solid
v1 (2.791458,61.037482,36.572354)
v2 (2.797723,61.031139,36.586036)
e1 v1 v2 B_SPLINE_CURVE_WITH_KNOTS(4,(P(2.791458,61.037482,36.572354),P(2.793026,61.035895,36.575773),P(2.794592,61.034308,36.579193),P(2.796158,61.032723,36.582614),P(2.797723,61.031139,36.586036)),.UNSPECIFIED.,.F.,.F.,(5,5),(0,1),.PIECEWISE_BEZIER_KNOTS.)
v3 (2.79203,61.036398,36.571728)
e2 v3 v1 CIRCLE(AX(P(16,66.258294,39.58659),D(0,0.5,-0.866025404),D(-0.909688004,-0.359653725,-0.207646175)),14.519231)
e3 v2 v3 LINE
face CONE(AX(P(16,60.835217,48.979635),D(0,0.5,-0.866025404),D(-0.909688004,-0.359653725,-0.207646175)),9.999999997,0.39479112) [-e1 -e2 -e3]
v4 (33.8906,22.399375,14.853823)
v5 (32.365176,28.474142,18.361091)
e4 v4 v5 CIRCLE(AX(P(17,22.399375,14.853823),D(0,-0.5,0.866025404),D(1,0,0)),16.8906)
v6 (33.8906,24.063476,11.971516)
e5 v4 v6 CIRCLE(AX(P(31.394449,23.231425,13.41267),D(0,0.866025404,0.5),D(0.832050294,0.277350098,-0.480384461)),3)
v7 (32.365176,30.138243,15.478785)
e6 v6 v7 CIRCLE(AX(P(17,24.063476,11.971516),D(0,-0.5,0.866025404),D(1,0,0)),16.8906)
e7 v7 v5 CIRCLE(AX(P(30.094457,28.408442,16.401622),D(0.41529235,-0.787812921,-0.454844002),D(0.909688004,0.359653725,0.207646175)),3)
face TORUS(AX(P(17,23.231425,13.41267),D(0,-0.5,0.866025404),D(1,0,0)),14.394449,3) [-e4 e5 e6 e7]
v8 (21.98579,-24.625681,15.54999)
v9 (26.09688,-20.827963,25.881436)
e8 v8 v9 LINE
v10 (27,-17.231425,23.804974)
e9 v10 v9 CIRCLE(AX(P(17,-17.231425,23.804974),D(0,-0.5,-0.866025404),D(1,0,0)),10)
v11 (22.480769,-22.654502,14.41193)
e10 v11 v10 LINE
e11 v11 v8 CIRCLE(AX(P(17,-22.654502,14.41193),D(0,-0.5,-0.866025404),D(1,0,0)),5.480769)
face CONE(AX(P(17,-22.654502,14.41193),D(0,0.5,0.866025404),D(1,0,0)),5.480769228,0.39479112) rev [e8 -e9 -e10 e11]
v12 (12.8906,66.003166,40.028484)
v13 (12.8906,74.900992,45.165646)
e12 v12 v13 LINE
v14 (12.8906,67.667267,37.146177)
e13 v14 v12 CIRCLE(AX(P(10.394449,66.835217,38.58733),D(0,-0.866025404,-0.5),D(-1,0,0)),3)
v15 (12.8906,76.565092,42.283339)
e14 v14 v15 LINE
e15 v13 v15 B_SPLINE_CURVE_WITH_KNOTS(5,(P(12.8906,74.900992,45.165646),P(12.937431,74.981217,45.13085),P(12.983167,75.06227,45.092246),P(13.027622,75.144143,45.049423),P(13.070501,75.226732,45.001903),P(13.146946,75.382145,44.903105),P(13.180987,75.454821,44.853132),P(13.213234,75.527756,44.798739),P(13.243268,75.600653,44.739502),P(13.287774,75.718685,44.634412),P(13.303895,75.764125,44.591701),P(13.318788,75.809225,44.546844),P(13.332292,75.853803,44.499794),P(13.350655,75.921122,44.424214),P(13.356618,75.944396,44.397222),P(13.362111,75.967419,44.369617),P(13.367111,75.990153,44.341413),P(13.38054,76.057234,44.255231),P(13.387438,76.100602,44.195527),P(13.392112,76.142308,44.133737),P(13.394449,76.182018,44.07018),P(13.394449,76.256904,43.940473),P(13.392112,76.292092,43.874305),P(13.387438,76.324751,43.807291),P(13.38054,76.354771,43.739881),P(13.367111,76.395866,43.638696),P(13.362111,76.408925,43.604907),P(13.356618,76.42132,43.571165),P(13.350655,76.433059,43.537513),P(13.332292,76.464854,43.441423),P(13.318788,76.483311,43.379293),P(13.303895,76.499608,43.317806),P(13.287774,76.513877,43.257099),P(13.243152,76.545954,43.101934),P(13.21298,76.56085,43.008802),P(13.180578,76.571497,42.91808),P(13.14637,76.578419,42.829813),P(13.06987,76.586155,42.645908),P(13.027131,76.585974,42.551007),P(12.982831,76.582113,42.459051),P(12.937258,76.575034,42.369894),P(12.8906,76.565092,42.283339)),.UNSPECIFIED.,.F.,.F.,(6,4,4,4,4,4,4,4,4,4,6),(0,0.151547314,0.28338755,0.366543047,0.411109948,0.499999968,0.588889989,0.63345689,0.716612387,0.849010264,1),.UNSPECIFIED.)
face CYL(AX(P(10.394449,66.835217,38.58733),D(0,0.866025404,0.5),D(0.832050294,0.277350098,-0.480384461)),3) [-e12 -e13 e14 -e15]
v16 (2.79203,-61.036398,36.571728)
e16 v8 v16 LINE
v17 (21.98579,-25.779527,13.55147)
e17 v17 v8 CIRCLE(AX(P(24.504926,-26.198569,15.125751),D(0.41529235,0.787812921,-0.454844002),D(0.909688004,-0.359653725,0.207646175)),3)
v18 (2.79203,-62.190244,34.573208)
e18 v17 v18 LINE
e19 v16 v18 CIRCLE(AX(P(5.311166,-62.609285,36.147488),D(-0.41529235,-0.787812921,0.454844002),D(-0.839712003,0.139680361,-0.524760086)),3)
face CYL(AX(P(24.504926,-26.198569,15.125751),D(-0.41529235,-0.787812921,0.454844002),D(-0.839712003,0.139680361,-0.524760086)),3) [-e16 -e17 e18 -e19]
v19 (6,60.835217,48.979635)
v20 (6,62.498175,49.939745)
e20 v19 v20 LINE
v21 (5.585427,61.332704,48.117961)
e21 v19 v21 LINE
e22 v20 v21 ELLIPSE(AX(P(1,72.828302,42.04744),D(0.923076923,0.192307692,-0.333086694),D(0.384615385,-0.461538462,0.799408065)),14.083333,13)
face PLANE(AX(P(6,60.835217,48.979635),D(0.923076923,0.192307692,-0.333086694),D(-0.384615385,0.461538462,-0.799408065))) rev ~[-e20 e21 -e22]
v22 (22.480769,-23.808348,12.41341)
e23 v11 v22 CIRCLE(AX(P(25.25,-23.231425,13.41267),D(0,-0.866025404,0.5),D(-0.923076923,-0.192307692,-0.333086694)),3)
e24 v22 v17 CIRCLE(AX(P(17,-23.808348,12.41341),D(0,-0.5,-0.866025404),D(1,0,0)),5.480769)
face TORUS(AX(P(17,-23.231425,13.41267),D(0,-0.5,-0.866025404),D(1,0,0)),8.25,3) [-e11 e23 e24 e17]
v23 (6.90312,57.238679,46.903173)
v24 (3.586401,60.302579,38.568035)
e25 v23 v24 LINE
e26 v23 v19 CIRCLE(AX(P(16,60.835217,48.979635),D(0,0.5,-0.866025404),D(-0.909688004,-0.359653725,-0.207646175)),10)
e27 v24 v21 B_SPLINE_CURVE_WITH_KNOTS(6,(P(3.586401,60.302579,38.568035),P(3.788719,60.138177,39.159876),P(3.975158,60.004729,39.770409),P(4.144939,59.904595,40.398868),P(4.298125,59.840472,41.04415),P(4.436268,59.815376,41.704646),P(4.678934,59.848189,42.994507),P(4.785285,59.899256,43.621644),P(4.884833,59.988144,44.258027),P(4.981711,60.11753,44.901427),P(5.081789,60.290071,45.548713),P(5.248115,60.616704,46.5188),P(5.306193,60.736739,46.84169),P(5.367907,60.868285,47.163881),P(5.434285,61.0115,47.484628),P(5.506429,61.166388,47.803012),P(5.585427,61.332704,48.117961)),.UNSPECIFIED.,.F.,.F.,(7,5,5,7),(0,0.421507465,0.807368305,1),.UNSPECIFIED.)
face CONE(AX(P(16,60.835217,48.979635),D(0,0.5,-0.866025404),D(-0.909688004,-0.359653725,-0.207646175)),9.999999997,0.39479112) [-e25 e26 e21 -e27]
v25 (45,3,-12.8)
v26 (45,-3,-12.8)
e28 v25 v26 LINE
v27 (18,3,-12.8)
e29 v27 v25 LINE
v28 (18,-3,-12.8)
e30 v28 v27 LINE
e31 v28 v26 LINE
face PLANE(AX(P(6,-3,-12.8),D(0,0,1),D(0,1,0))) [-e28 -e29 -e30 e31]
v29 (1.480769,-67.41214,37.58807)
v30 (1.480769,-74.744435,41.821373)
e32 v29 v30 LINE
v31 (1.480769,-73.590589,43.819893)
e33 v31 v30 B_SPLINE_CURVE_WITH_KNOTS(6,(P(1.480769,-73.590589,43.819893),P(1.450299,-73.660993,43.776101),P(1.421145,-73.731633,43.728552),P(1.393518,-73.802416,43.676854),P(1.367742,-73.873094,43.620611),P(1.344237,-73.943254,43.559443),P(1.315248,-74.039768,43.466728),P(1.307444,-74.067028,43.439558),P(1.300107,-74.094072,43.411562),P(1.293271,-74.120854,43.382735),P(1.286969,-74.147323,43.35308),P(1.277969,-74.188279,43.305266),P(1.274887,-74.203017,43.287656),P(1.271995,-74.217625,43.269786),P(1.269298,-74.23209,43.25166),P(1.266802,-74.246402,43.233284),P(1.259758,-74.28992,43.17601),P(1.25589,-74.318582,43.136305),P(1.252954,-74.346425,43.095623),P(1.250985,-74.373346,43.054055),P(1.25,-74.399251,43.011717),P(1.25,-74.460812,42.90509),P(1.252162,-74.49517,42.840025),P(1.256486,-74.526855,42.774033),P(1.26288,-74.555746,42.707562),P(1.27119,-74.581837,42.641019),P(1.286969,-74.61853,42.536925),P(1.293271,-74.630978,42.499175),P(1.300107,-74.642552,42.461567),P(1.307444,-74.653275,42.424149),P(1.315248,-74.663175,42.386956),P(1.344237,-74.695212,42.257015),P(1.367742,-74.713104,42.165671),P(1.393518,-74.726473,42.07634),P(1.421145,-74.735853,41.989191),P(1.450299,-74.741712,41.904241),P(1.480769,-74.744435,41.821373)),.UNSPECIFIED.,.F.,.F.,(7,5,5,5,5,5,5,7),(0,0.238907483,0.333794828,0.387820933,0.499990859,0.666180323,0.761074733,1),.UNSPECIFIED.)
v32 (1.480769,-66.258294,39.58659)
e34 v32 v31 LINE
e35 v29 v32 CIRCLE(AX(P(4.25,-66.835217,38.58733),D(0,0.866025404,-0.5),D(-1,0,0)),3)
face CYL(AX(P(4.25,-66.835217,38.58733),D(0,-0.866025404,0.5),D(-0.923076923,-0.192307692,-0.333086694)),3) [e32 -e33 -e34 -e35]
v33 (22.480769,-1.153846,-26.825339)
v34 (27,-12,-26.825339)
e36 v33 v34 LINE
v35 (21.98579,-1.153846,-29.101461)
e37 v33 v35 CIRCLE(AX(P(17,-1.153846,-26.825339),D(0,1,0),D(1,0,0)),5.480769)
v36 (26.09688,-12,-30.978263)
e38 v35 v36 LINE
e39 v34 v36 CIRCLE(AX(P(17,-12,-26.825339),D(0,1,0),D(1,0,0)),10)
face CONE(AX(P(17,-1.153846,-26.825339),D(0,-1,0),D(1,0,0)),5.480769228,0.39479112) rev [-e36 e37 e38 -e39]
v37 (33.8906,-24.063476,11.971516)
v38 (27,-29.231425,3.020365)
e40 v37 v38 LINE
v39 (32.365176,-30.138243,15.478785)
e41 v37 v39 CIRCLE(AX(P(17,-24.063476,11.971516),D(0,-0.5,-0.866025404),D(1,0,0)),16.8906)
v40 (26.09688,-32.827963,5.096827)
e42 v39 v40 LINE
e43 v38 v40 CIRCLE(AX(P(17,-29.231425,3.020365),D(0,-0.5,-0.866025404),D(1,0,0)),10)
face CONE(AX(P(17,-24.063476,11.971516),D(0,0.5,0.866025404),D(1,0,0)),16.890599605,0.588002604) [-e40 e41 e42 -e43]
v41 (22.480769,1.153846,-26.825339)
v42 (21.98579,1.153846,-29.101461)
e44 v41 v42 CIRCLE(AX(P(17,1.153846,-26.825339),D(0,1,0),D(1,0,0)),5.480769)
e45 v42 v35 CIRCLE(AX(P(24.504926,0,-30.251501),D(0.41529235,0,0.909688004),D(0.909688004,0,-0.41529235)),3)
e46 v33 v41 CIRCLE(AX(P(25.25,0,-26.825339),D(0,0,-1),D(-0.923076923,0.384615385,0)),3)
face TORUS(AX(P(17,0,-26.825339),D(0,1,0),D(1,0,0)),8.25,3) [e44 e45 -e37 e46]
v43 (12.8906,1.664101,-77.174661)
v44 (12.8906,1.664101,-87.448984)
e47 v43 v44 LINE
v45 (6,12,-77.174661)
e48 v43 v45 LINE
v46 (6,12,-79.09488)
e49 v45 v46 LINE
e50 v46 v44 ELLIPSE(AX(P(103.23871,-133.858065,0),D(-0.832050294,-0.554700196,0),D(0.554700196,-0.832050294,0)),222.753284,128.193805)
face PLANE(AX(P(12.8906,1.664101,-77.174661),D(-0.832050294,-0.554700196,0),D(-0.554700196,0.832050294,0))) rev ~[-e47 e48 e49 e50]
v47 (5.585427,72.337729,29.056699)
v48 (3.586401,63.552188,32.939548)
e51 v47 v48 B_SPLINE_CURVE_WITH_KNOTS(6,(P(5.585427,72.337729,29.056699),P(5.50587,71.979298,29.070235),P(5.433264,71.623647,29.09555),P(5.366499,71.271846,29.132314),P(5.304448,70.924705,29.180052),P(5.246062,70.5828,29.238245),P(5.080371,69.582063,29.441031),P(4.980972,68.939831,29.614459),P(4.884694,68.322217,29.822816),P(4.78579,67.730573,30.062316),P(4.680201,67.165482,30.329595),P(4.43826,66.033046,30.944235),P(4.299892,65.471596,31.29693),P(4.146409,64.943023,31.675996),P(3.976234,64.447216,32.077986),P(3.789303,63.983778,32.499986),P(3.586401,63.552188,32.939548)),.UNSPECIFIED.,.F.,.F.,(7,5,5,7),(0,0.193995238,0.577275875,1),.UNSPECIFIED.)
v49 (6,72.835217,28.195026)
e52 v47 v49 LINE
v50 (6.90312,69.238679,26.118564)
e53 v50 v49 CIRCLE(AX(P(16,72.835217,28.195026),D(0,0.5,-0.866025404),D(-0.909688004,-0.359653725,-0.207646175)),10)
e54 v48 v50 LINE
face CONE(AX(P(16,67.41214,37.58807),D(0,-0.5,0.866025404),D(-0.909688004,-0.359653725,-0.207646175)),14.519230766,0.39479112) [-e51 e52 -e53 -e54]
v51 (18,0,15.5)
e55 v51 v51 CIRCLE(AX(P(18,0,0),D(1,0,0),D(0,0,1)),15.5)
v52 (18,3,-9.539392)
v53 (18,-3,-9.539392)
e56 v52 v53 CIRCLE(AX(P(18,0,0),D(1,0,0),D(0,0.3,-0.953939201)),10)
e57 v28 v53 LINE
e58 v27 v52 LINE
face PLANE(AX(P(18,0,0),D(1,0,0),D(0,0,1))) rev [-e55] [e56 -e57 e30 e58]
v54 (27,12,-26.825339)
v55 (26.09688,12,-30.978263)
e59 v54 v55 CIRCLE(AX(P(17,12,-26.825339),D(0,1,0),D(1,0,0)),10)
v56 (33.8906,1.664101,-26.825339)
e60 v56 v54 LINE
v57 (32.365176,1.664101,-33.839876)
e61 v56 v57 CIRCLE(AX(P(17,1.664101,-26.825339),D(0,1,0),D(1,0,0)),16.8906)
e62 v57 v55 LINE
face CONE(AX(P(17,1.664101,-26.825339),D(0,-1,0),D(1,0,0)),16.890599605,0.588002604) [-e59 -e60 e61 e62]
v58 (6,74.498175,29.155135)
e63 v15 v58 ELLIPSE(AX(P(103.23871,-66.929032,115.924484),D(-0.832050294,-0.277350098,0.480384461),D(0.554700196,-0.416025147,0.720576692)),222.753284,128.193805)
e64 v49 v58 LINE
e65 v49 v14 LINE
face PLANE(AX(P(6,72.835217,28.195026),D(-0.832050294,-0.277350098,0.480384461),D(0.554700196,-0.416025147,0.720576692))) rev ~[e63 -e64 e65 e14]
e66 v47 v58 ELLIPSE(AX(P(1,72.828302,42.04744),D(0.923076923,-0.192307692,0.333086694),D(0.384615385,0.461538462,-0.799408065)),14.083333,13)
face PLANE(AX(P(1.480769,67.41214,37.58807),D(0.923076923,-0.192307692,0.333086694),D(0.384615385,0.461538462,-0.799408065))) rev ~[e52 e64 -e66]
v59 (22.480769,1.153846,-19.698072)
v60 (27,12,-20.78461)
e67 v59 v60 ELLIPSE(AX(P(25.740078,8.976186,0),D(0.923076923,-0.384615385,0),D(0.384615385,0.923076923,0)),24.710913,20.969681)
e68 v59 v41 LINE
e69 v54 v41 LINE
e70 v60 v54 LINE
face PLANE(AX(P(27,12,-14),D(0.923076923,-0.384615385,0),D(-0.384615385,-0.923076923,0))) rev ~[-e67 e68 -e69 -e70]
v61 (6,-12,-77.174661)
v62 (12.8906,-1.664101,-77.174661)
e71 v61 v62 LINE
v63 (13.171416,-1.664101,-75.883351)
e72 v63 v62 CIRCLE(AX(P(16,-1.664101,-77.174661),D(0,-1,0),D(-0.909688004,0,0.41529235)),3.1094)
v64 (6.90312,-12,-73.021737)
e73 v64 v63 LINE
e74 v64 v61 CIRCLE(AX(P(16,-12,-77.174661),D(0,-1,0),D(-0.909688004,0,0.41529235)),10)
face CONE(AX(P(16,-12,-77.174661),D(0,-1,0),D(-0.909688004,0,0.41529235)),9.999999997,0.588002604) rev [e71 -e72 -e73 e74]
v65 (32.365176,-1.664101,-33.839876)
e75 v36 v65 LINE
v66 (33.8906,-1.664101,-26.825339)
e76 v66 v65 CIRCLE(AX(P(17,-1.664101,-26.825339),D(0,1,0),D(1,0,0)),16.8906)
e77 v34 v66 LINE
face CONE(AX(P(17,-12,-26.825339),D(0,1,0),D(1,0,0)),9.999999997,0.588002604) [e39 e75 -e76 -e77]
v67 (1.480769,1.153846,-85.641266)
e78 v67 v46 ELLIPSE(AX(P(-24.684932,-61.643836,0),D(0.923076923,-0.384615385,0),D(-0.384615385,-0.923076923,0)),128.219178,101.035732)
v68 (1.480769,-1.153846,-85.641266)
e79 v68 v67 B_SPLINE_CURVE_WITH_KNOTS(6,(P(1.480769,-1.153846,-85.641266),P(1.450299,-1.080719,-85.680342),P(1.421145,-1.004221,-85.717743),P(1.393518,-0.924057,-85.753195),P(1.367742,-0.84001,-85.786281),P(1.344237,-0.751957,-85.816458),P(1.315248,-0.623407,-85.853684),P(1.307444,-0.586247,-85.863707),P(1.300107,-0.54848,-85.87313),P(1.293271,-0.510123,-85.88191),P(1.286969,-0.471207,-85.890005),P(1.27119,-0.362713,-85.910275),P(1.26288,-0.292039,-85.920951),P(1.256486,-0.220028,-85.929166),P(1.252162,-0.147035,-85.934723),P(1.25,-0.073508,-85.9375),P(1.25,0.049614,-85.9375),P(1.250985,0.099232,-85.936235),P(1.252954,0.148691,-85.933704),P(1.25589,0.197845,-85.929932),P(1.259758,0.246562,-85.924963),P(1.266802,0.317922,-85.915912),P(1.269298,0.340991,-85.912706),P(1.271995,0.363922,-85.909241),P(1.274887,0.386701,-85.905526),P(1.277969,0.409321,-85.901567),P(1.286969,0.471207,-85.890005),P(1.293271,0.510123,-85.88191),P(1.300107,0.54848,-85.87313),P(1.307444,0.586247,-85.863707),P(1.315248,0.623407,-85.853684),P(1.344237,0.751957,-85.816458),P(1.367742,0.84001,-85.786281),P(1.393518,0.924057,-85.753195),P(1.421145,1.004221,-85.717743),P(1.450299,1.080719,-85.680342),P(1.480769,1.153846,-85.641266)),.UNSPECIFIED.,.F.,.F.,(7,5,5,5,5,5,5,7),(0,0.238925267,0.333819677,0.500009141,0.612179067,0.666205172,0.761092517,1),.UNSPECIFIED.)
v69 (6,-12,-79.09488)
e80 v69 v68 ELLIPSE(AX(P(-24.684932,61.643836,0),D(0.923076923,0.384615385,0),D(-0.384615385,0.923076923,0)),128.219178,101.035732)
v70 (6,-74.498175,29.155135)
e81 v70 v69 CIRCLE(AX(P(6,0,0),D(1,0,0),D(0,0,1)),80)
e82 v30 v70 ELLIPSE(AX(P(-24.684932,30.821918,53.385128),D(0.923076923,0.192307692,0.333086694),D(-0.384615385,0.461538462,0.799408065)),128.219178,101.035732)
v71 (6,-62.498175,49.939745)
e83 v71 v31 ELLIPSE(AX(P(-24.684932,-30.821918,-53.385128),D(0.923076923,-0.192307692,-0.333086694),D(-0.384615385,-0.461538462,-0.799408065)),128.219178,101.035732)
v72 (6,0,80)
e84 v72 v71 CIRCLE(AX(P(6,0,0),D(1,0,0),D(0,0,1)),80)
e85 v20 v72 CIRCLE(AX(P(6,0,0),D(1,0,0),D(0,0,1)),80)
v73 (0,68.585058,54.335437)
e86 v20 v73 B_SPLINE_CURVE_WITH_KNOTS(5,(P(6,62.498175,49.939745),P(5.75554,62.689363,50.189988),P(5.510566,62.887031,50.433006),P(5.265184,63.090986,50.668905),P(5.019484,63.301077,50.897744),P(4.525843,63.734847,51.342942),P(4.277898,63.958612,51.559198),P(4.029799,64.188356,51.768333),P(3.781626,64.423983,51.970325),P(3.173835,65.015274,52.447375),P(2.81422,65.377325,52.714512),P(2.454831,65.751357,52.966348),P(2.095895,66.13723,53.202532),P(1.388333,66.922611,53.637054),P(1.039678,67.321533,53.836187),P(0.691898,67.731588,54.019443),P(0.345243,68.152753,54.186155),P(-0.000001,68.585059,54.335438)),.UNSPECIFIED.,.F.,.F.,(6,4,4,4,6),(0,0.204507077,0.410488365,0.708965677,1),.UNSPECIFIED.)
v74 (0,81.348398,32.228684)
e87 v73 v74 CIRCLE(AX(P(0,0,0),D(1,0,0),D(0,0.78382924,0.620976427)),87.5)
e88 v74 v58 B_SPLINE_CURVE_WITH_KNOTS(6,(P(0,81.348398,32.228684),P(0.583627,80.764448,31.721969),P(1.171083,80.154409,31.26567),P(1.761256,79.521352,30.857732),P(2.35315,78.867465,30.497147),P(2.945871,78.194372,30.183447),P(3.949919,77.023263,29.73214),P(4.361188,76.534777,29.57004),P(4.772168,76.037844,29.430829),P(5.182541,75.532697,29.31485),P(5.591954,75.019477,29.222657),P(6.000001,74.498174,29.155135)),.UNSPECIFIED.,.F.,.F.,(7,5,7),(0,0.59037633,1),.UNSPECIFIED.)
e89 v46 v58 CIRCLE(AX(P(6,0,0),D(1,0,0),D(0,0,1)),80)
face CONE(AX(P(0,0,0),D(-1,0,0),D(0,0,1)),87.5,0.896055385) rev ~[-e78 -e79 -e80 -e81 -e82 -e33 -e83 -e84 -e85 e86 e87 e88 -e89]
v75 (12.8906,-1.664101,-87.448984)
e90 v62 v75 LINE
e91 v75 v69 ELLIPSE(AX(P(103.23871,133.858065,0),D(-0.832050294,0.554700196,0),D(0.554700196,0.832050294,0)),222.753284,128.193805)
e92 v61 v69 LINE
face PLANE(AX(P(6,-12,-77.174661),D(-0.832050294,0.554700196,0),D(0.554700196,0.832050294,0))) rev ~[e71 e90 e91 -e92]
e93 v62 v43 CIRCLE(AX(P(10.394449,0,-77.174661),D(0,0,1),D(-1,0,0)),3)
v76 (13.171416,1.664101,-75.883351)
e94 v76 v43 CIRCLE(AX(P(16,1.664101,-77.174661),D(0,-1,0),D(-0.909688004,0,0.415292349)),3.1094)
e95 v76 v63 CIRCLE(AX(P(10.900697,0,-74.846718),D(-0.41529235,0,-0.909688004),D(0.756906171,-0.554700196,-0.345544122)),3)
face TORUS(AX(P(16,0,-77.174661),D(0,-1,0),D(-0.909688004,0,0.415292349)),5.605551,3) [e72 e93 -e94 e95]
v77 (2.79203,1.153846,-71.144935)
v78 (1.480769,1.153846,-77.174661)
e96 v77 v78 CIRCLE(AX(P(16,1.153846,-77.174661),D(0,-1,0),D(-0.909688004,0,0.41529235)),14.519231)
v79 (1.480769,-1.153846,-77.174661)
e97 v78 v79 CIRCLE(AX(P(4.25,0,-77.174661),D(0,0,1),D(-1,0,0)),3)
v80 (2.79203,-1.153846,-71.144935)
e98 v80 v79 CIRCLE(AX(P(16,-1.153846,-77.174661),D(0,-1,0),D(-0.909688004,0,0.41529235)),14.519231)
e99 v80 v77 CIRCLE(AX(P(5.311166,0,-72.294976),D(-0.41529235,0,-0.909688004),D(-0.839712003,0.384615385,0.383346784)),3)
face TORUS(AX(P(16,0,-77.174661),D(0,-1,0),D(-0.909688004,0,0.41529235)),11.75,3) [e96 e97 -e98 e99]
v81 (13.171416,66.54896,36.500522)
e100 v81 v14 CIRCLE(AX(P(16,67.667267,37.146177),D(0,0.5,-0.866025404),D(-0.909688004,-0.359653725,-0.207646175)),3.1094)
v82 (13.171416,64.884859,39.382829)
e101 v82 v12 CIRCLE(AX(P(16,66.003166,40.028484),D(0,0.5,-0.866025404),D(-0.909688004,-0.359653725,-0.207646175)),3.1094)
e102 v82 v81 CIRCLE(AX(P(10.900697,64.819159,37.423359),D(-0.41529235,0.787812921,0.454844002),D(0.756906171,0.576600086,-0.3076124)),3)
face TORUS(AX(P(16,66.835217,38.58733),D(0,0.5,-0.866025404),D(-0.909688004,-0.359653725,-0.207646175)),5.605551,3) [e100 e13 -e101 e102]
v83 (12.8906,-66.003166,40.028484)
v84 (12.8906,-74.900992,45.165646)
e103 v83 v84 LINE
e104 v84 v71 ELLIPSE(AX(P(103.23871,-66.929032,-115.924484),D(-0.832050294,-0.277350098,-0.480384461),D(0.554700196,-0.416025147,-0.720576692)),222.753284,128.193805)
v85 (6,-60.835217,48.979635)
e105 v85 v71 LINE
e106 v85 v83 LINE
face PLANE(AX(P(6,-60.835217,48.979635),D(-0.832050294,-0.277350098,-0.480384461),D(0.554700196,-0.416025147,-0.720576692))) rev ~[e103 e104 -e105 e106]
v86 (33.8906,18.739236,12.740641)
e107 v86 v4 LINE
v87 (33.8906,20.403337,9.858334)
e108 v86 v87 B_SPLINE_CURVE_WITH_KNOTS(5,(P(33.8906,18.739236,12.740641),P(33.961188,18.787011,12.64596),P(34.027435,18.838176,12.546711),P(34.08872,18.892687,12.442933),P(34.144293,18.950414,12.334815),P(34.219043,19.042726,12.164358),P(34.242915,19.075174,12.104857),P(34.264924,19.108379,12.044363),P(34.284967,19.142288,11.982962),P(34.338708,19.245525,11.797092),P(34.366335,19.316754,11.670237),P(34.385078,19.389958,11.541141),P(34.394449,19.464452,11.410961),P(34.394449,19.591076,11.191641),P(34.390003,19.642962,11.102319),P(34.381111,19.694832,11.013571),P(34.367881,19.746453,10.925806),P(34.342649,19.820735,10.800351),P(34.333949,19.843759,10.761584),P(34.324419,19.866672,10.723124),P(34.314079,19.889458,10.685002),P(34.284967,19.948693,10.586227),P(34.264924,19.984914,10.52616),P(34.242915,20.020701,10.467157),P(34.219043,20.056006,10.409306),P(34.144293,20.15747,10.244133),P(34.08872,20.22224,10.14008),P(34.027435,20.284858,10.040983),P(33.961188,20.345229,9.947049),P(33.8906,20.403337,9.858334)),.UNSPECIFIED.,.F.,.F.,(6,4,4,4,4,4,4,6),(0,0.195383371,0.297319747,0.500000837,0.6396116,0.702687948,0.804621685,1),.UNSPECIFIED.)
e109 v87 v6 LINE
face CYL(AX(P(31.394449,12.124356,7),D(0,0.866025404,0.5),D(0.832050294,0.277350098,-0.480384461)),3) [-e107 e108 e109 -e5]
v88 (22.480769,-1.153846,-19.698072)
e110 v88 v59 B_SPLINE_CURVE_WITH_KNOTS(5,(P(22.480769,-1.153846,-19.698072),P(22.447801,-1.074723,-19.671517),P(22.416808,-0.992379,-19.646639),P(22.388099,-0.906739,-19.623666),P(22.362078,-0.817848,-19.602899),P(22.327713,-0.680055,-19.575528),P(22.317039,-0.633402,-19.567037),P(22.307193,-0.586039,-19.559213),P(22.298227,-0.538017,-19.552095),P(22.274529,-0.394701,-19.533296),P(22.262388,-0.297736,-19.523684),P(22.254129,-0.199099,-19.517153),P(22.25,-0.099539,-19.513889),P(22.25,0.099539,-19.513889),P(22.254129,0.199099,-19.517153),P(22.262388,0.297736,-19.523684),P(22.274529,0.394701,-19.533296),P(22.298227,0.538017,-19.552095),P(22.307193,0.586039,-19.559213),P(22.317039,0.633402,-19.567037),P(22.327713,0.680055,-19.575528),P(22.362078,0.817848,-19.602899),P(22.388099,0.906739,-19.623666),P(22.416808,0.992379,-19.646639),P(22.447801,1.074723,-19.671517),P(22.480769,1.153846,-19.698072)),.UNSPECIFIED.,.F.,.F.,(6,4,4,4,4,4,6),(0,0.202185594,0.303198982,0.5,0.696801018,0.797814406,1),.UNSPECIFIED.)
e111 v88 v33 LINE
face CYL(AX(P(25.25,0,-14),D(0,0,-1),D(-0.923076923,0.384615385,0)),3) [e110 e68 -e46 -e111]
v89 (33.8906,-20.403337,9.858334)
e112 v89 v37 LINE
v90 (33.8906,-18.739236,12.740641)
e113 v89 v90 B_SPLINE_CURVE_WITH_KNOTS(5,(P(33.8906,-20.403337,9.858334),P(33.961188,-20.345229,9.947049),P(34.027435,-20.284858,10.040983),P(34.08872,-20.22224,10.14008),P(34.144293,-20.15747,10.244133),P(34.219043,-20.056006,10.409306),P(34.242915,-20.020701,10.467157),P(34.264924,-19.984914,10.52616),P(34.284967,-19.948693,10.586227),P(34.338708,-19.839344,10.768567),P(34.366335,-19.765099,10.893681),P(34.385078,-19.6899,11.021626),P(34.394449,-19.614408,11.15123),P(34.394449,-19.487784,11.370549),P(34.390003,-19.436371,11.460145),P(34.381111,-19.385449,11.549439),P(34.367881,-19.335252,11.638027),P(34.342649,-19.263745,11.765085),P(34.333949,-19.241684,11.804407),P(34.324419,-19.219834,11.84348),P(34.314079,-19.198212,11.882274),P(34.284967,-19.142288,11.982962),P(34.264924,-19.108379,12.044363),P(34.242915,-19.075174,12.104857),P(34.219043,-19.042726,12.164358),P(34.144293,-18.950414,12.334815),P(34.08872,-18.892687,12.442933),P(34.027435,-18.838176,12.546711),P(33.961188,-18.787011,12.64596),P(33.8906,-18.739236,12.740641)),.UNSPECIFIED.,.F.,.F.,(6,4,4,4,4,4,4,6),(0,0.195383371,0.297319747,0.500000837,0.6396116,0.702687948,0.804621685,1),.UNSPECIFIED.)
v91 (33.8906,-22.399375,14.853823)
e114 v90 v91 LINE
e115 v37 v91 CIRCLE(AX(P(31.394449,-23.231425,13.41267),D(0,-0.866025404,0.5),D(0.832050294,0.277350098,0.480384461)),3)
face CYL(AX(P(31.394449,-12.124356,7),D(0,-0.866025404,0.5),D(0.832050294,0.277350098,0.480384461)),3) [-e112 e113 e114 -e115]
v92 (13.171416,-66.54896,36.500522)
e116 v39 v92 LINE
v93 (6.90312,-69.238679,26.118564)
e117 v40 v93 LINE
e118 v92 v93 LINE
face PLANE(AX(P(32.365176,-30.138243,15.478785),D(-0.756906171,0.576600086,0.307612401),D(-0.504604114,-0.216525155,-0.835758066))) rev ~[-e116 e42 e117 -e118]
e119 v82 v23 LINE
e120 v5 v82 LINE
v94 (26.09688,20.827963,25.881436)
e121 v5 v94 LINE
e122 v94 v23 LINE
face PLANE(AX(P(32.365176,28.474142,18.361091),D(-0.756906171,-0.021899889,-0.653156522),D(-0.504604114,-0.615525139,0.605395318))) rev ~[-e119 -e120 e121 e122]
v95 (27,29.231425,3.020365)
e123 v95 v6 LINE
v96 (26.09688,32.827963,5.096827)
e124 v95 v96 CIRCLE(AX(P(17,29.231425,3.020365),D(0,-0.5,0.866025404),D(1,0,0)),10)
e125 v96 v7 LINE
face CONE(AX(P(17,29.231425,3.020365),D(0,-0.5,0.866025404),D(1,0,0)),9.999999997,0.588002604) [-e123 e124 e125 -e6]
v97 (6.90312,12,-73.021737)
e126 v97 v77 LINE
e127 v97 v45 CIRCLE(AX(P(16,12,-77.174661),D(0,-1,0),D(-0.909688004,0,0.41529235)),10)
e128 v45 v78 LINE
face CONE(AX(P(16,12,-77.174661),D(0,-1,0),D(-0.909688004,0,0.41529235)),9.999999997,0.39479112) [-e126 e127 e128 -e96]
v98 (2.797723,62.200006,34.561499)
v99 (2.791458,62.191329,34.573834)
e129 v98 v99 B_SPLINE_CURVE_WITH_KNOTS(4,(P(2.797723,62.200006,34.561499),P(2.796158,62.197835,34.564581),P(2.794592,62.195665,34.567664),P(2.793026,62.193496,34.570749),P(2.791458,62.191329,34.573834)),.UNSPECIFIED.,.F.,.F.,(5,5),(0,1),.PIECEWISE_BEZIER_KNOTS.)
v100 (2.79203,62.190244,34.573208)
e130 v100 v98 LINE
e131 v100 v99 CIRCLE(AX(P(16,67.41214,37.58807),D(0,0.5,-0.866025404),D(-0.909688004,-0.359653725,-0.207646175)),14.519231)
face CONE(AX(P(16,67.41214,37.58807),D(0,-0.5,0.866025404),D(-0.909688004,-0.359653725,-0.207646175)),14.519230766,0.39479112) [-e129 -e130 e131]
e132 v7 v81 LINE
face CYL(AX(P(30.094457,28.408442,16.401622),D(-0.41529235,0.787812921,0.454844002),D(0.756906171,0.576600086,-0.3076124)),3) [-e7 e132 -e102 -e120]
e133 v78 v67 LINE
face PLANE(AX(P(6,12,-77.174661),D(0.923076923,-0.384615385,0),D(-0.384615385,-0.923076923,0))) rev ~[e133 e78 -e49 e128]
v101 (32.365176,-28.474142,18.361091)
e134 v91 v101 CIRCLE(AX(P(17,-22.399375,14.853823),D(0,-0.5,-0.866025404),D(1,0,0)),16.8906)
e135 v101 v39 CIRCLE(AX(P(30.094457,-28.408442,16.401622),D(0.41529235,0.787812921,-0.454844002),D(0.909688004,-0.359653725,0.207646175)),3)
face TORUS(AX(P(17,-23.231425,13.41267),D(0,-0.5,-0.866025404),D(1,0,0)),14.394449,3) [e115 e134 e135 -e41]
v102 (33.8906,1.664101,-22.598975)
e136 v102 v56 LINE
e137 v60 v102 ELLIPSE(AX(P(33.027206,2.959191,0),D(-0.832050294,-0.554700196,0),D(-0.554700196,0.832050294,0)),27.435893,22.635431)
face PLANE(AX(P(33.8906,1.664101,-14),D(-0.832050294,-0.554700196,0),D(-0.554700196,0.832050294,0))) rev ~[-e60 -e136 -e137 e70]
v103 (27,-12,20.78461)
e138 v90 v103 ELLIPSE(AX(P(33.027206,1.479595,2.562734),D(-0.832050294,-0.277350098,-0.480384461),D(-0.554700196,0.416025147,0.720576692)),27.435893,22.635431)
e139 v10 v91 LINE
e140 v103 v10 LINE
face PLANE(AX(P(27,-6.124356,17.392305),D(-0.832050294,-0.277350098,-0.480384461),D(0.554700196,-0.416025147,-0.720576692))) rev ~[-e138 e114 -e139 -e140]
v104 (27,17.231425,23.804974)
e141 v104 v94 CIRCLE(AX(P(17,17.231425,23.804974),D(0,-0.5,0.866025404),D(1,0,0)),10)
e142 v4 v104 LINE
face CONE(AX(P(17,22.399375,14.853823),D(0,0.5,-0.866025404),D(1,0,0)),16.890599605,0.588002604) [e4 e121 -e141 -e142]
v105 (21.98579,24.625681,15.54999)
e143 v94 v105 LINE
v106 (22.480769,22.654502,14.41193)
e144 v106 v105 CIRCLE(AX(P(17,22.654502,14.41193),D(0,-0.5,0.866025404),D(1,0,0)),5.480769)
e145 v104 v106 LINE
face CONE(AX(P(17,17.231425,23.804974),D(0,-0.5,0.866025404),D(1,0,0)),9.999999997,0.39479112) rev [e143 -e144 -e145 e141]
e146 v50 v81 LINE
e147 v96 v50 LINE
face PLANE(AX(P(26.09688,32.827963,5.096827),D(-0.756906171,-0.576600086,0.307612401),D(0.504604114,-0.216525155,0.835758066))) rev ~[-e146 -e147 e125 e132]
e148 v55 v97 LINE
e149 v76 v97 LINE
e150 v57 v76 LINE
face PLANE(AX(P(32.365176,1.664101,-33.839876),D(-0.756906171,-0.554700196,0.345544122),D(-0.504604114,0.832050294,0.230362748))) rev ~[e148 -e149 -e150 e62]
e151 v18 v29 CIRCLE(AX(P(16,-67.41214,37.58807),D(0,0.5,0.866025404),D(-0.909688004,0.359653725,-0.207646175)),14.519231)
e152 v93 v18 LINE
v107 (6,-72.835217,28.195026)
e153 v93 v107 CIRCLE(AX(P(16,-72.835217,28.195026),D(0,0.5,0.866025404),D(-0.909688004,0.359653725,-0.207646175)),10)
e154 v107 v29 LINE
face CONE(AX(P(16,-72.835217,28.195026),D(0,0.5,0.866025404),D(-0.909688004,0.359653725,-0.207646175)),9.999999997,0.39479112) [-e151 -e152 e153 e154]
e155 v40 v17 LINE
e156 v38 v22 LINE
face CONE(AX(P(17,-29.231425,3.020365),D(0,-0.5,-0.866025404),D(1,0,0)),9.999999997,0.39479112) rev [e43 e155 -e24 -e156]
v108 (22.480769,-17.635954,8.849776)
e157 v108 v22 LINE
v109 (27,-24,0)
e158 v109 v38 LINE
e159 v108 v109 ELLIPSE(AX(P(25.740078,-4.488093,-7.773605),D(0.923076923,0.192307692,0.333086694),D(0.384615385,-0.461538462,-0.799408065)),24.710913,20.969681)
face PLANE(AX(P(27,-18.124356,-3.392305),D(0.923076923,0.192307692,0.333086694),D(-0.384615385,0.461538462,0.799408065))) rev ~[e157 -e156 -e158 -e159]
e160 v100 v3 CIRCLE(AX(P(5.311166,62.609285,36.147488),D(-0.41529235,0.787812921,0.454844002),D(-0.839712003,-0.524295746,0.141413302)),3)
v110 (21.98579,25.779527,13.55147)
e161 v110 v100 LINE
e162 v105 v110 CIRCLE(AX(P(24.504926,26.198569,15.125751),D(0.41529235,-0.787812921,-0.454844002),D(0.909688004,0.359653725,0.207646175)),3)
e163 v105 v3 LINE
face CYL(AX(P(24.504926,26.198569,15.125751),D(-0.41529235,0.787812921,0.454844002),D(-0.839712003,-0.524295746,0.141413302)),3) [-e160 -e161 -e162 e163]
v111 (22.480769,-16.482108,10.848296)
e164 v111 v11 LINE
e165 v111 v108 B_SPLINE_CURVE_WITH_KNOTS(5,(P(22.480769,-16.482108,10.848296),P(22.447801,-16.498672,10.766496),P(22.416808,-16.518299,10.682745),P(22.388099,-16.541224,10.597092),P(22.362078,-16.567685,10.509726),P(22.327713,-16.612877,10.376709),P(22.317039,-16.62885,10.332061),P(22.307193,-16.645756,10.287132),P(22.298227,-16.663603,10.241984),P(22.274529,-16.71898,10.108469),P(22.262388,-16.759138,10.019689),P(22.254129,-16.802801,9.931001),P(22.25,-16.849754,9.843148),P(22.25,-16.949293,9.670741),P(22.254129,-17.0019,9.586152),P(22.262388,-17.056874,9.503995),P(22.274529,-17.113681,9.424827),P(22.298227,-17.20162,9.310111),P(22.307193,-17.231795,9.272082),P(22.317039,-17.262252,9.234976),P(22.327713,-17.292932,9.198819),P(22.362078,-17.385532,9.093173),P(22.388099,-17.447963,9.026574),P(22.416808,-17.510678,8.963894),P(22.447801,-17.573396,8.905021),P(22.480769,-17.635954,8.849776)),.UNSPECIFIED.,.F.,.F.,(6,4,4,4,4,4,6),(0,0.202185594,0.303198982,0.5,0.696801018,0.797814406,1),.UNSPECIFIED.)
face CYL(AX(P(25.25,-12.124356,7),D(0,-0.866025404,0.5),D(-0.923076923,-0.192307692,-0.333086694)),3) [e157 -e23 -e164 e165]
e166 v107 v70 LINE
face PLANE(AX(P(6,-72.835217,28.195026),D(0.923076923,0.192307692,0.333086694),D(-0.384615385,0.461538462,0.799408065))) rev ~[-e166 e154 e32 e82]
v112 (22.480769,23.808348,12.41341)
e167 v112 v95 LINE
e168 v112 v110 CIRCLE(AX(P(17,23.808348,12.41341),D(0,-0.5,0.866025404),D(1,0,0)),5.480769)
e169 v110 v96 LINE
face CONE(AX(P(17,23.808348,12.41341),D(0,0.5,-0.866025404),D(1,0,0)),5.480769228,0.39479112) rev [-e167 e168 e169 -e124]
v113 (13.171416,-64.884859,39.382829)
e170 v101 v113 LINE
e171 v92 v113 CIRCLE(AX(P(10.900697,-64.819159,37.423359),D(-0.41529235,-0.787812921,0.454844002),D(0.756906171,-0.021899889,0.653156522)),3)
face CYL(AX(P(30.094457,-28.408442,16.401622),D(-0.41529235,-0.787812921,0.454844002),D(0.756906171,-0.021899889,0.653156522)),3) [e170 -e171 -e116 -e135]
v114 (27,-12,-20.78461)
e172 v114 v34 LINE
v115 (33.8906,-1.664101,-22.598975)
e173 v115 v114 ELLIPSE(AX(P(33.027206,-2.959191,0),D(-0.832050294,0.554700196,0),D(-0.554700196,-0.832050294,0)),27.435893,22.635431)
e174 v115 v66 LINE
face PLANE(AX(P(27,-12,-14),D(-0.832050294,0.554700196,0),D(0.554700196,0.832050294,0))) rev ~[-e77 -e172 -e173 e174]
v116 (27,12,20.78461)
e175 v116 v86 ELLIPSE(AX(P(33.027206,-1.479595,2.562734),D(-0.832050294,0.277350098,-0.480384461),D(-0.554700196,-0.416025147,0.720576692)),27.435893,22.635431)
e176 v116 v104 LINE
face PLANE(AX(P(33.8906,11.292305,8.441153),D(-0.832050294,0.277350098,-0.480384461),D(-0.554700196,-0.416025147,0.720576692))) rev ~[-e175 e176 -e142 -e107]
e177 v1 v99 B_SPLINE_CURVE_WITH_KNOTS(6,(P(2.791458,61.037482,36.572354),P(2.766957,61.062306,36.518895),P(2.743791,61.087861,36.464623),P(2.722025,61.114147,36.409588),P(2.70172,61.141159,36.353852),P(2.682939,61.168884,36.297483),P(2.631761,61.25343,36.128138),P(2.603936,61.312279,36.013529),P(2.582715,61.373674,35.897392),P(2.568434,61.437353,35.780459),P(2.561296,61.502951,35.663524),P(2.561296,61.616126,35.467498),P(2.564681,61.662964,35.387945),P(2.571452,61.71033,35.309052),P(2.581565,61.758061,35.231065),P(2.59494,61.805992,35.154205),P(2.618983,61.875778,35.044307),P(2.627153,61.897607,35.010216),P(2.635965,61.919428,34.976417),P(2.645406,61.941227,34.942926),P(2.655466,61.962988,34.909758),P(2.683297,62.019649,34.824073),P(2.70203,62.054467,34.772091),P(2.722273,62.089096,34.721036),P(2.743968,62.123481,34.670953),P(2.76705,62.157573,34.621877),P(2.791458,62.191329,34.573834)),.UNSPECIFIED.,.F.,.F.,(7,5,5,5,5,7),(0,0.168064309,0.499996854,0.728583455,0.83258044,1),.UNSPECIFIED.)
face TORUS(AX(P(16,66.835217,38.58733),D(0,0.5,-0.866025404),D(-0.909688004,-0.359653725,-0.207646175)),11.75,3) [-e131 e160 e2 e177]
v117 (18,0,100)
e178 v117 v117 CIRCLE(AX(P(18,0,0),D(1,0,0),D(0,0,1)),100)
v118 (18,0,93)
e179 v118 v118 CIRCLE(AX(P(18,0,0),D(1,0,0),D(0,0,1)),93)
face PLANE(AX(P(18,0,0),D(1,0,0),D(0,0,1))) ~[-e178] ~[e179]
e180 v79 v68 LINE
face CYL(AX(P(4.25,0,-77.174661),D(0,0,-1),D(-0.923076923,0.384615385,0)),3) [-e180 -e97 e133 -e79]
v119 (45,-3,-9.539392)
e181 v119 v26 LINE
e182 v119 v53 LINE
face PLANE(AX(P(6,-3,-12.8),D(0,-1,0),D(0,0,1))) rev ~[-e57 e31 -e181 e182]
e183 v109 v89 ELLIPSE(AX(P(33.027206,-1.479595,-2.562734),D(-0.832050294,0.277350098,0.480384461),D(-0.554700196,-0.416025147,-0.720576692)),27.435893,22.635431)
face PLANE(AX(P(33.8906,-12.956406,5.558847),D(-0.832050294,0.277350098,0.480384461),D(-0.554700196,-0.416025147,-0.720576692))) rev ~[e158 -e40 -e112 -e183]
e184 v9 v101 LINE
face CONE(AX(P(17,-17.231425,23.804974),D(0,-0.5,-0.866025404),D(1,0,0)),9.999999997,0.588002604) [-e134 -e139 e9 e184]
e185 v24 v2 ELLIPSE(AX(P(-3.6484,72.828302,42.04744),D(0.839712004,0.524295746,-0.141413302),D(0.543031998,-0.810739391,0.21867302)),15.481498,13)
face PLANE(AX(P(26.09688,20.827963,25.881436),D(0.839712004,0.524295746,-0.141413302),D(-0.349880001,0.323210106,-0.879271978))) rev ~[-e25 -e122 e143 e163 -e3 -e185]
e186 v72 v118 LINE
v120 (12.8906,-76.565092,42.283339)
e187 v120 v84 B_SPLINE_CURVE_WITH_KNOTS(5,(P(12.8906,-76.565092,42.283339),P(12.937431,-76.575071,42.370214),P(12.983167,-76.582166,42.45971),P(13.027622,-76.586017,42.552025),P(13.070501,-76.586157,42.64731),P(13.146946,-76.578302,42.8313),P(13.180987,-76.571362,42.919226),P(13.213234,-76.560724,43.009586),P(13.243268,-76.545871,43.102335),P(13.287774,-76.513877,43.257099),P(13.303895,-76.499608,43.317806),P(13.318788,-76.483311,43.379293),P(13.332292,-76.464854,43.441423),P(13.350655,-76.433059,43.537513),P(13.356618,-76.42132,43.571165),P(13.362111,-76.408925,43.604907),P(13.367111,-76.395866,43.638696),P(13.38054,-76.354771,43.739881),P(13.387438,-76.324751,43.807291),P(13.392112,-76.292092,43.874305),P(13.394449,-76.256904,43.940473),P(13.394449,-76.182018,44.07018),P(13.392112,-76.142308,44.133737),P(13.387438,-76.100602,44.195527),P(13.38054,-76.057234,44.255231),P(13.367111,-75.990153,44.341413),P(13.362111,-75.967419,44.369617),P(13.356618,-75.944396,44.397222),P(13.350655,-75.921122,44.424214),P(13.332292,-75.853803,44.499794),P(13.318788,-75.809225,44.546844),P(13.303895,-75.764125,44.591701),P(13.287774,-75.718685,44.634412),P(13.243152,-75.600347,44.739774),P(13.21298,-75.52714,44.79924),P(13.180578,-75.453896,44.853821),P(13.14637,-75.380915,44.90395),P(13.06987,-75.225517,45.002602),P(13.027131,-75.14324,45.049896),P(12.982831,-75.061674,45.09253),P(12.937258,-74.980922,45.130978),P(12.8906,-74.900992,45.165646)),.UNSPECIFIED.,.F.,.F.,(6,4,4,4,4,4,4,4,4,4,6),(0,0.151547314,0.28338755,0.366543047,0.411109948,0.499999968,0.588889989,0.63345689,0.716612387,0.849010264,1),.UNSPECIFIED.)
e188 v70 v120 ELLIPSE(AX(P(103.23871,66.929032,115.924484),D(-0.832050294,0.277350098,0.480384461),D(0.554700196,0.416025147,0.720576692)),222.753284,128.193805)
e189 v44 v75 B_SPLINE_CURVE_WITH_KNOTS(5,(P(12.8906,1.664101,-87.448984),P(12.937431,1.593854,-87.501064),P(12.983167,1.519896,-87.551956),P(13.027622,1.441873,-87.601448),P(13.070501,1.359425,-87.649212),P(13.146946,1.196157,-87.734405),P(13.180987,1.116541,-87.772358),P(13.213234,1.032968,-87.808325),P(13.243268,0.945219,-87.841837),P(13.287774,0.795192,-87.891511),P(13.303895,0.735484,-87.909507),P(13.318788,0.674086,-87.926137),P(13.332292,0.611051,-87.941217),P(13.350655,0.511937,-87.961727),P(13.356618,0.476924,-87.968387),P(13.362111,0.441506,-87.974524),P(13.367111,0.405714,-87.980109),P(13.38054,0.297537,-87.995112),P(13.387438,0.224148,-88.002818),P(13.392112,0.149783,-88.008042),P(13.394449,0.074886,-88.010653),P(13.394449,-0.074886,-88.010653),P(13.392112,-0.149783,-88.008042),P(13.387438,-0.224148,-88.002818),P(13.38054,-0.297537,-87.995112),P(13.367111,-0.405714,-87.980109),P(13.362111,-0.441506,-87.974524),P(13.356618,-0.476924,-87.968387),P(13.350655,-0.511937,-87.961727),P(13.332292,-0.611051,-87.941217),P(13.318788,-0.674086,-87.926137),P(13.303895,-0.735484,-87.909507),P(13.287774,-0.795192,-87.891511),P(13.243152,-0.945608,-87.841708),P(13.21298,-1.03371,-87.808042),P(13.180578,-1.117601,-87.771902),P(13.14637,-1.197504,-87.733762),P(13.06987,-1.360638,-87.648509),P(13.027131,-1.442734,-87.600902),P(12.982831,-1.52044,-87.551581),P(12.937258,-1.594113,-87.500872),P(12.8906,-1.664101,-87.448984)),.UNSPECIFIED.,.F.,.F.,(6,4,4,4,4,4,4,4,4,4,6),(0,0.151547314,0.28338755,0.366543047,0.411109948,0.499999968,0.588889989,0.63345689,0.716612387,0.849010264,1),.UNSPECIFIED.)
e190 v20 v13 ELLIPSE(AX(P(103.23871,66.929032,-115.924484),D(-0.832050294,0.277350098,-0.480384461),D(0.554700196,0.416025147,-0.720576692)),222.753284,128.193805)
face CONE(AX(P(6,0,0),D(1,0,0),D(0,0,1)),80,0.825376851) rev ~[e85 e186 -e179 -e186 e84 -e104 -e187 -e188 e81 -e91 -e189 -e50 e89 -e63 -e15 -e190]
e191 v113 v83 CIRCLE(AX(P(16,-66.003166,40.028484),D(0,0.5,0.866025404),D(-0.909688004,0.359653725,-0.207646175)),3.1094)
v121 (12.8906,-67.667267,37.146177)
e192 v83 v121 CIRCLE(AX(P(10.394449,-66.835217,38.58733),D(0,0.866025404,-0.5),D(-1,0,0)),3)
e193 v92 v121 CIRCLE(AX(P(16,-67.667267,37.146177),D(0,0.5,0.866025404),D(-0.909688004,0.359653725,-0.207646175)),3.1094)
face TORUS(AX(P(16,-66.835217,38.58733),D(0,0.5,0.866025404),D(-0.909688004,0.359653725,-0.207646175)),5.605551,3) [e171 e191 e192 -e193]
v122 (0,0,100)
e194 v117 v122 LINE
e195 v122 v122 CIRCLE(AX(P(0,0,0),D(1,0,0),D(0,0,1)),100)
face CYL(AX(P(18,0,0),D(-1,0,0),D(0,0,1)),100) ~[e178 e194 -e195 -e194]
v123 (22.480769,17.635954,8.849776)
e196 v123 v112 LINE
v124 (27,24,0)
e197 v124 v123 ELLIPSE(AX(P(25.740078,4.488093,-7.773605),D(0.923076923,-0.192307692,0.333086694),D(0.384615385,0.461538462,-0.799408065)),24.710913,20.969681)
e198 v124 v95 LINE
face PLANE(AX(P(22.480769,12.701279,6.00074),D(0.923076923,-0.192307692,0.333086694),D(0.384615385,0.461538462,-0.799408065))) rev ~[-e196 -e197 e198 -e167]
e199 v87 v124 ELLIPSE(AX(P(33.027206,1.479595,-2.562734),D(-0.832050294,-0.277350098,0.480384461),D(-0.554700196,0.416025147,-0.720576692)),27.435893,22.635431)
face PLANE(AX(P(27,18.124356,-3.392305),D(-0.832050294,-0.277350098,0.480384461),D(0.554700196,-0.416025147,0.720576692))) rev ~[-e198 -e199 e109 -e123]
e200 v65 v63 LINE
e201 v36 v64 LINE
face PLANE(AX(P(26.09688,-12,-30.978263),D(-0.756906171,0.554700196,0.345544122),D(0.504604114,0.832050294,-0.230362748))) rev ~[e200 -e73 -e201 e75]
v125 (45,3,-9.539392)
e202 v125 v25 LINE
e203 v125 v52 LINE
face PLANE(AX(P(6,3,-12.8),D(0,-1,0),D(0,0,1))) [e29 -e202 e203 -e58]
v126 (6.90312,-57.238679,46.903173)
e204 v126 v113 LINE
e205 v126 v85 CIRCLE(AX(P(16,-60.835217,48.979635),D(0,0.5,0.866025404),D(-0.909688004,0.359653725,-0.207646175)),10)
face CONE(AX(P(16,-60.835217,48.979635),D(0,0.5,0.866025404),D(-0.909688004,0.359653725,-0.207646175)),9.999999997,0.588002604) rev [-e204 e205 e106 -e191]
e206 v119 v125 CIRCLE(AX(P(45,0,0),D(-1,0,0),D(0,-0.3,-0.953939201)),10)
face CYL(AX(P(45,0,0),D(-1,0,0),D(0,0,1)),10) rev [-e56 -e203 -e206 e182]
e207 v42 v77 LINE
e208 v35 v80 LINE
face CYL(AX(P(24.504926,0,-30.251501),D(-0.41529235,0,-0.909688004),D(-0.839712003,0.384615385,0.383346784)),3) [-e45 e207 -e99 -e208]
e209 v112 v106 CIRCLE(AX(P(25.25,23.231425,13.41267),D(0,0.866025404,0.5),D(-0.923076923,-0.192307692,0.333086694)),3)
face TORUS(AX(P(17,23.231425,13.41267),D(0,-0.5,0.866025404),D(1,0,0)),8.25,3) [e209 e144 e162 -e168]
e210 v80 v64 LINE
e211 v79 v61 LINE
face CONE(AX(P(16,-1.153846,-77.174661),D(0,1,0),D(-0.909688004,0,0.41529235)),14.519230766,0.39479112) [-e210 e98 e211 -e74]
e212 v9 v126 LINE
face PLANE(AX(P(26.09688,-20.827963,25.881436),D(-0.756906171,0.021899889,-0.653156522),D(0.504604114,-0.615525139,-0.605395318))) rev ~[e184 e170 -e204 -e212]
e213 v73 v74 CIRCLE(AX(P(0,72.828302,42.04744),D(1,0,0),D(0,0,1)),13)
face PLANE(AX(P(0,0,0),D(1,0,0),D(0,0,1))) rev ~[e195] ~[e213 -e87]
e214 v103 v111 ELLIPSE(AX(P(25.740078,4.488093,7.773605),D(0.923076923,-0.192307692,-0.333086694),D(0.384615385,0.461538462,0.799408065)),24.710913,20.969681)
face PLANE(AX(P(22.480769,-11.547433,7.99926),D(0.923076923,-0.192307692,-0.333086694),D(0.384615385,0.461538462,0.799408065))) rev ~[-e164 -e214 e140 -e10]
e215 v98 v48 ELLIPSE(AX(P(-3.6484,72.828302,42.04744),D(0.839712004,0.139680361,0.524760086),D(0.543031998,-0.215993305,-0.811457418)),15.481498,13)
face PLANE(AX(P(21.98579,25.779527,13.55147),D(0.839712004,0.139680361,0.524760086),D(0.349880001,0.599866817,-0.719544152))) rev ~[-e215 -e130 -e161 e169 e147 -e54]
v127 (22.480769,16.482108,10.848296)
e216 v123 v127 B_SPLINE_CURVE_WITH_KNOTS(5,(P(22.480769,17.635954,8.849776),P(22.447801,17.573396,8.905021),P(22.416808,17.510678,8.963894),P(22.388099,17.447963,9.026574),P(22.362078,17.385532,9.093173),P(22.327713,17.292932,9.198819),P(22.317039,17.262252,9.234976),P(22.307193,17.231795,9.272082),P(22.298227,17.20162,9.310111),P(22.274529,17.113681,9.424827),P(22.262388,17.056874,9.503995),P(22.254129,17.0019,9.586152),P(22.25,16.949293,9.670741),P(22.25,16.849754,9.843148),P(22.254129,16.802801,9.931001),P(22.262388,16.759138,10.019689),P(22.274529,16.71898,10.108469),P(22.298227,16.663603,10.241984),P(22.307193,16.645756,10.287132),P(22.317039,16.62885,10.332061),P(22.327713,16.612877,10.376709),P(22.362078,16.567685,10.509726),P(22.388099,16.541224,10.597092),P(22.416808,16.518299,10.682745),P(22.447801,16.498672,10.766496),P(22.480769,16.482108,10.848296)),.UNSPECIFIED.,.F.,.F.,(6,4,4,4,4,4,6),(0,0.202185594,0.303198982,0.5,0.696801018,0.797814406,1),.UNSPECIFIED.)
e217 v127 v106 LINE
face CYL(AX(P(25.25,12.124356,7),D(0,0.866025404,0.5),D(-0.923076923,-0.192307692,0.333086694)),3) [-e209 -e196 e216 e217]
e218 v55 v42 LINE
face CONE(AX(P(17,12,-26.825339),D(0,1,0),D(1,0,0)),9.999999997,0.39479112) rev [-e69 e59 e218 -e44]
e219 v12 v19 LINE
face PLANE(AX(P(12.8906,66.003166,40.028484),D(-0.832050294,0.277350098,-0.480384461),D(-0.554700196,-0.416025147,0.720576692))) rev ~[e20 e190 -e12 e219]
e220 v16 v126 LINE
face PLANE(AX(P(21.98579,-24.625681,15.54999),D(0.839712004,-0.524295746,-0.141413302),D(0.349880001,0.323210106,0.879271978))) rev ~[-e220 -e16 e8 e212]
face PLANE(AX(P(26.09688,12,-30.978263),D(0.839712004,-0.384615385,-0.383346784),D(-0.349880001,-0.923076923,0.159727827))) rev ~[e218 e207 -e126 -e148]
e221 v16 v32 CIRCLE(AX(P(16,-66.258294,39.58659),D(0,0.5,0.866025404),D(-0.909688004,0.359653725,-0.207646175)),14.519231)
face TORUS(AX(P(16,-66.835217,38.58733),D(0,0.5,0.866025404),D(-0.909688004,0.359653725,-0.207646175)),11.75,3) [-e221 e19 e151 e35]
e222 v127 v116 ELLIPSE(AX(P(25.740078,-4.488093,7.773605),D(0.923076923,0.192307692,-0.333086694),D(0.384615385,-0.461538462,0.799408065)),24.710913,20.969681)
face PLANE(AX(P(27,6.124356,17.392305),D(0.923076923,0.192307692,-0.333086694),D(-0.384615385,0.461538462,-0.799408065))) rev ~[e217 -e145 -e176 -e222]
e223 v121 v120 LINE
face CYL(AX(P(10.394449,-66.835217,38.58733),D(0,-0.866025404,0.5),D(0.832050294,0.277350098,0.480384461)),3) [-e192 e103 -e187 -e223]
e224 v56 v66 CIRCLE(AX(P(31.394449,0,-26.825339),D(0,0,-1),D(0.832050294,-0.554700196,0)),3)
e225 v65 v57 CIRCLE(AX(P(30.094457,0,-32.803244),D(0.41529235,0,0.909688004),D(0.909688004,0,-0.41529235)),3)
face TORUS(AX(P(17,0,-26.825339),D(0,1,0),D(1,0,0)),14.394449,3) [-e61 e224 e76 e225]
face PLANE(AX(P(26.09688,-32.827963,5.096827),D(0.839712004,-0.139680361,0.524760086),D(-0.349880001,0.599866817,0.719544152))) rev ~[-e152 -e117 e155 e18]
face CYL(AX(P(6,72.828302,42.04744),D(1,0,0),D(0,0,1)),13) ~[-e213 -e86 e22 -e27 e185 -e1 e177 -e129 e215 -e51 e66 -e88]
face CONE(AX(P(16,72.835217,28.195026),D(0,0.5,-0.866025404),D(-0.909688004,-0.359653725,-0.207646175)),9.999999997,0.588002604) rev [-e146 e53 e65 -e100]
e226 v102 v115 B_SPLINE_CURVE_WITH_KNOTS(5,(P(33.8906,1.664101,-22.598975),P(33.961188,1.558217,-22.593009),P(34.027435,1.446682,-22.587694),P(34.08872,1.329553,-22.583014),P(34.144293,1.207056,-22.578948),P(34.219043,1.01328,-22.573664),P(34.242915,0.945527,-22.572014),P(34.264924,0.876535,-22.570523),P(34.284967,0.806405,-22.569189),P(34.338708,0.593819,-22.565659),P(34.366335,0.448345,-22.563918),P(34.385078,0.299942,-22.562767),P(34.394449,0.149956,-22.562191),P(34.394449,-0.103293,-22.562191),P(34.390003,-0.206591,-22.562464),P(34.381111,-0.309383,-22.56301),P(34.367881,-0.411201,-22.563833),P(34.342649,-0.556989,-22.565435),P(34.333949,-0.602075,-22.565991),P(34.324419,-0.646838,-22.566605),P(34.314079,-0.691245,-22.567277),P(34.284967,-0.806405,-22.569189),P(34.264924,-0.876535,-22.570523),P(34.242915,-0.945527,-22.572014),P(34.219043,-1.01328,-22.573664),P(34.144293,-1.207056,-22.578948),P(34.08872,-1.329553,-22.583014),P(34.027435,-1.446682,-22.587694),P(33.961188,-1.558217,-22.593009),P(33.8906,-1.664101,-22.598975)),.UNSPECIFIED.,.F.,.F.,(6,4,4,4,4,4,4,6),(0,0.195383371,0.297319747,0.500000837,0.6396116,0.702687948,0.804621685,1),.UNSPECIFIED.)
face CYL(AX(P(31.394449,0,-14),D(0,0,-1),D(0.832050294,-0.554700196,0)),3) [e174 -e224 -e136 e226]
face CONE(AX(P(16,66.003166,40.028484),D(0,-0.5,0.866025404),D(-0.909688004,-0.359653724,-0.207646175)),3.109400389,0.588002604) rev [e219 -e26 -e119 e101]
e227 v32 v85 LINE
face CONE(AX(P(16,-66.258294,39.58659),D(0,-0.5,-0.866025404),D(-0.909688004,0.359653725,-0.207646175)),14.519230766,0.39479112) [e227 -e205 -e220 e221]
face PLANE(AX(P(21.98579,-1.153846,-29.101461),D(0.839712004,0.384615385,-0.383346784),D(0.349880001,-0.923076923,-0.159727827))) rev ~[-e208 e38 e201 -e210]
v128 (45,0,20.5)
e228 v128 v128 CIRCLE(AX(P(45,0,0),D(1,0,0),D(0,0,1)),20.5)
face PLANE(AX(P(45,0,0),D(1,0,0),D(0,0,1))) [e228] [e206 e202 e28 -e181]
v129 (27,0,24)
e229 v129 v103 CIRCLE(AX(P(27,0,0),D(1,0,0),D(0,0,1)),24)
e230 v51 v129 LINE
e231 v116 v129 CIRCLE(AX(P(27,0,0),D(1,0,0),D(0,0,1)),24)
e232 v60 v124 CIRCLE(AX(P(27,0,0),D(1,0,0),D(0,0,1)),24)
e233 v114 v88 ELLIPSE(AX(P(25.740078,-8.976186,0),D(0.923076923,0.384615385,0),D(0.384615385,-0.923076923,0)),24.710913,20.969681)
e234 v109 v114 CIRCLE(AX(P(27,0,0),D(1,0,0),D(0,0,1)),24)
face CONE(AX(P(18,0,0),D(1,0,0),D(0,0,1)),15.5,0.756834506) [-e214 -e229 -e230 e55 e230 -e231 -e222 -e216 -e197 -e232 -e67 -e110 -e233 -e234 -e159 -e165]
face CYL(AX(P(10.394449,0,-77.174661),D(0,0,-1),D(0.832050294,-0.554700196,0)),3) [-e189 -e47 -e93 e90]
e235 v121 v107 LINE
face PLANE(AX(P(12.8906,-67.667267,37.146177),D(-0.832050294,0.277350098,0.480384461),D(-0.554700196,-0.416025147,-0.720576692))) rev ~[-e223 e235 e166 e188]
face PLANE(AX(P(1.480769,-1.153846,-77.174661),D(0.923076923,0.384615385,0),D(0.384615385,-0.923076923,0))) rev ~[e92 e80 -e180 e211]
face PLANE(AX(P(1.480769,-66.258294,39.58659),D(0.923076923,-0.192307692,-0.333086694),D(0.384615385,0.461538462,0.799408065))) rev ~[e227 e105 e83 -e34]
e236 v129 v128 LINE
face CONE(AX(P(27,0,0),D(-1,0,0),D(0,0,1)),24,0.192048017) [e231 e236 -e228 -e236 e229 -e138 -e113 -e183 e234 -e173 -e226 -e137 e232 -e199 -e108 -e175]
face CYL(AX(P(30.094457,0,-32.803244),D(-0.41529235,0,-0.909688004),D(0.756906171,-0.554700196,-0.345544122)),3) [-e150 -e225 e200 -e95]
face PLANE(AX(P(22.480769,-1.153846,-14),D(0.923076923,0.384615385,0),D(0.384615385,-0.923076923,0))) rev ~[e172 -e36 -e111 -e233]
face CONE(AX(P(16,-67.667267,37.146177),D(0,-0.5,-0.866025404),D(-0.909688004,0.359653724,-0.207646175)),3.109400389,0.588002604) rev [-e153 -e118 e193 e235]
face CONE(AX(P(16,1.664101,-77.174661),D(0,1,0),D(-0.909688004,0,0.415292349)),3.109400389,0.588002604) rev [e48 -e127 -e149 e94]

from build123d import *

# Parameters (mm, degrees)
PATTERN_CIRCULAR_1_COUNT = 3
EXTRUDE_1_REACH          = 148.7
SKETCH_4_R               = 13
SKETCH_5_W               = 5
SKETCH_5_H               = 6
CUT_EXTRUDE_1_DEPTH      = 147.700374941


with BuildPart() as part:
    # 草图1 → 旋转1 (revolve)
    with BuildSketch(Plane.XY, mode=Mode.PRIVATE) as revolve_1_sk:
        Polygon((0, 100), (0, 87.5), (6, 80), (18, 93), (18, 100), align=None)
        Polygon((27, 24), (45, 20.5), (45, 10), (18, 10), (18, 15.5), align=None)
    revolve(revolve_1_sk.sketch.rotate(Axis((0, 0, 0), (1, 0, 0)), 90), axis=Axis((0, 0, 0), (1, 0, 0)))

    # 扫描4: sweep along a path in 草图3
    with BuildLine(Plane(origin=(0, 0, 0), x_dir=(1, 0, 0), z_dir=(0, 1, 0))) as sweep_4_path:
        Line((27, 14), (27, 24))
        Line((27, 24), (27, 26.825339277))
        ThreePointArc((27, 26.825339277), (26.771611955, 28.950333349), (26.096880039, 30.978262773))
        Line((26.096880039, 30.978262773), (6.903119961, 73.021737227))
        ThreePointArc((6.903119961, 73.021737227), (6.228388045, 75.049666651), (6, 77.174660723))
        Line((6, 77.174660723), (6, 80))
        Line((6, 80), (6, 90))
    # 草图2 → 扫描4 (sweep)
    with BuildSketch(Plane.XY.offset(-14)):
        with BuildLine():
            Line((27, 12), (22.480769231, 1.153846154))
            ThreePointArc((22.480769231, 1.153846154), (22.25, 0), (22.480769231, -1.153846154))
            Line((22.480769231, -1.153846154), (27, -12))
            Line((27, -12), (33.890599608, -1.664100589))
            ThreePointArc((33.890599608, -1.664100589), (34.394448725, 0), (33.890599608, 1.664100589))
            Line((33.890599608, 1.664100589), (27, 12))
        make_face()
    sweep_4 = sweep(path=sweep_4_path.line)

    # 阵列(圆周)1: 扫描4 ×3 about axis
    pattern_circular_1_axis = Axis((0, 0, 0), (1, 0, 0))
    for i in range(1, PATTERN_CIRCULAR_1_COUNT):
        add(sweep_4.rotate(pattern_circular_1_axis, i * 360 / PATTERN_CIRCULAR_1_COUNT))

    # 凸台-拉伸1: up to this face of the body (flat: up to its plane)
    extrude_1_end = Plane(part.part.faces().sort_by_distance((0, 0, -97.171572875))[0])
    # 草图4 → 凸台-拉伸1 (add, up to the picked face)
    with BuildSketch(Plane.ZY.offset(-6), mode=Mode.PRIVATE) as extrude_1_sk1:
        with Locations((42.047439865, 72.828302174)):
            Circle(SKETCH_4_R)
    extrude_1_tool1 = split(extrude(extrude_1_sk1.sketch, amount=EXTRUDE_1_REACH, mode=Mode.PRIVATE), bisect_by=extrude_1_end, keep=Keep.BOTH, mode=Mode.PRIVATE)
    add(extrude_1_tool1.solids().sort_by(Axis((6, 72.828302, 42.04744), (-1, 0, 0)))[0])

    # 草图5 → 切除-拉伸1 (cut, through all)
    with BuildSketch(Plane.ZY.offset(-6)):
        with Locations((-10.3, 0)):
            Rectangle(SKETCH_5_W, SKETCH_5_H)
    extrude(amount=-CUT_EXTRUDE_1_DEPTH, mode=Mode.SUBTRACT)


solid = part.part
